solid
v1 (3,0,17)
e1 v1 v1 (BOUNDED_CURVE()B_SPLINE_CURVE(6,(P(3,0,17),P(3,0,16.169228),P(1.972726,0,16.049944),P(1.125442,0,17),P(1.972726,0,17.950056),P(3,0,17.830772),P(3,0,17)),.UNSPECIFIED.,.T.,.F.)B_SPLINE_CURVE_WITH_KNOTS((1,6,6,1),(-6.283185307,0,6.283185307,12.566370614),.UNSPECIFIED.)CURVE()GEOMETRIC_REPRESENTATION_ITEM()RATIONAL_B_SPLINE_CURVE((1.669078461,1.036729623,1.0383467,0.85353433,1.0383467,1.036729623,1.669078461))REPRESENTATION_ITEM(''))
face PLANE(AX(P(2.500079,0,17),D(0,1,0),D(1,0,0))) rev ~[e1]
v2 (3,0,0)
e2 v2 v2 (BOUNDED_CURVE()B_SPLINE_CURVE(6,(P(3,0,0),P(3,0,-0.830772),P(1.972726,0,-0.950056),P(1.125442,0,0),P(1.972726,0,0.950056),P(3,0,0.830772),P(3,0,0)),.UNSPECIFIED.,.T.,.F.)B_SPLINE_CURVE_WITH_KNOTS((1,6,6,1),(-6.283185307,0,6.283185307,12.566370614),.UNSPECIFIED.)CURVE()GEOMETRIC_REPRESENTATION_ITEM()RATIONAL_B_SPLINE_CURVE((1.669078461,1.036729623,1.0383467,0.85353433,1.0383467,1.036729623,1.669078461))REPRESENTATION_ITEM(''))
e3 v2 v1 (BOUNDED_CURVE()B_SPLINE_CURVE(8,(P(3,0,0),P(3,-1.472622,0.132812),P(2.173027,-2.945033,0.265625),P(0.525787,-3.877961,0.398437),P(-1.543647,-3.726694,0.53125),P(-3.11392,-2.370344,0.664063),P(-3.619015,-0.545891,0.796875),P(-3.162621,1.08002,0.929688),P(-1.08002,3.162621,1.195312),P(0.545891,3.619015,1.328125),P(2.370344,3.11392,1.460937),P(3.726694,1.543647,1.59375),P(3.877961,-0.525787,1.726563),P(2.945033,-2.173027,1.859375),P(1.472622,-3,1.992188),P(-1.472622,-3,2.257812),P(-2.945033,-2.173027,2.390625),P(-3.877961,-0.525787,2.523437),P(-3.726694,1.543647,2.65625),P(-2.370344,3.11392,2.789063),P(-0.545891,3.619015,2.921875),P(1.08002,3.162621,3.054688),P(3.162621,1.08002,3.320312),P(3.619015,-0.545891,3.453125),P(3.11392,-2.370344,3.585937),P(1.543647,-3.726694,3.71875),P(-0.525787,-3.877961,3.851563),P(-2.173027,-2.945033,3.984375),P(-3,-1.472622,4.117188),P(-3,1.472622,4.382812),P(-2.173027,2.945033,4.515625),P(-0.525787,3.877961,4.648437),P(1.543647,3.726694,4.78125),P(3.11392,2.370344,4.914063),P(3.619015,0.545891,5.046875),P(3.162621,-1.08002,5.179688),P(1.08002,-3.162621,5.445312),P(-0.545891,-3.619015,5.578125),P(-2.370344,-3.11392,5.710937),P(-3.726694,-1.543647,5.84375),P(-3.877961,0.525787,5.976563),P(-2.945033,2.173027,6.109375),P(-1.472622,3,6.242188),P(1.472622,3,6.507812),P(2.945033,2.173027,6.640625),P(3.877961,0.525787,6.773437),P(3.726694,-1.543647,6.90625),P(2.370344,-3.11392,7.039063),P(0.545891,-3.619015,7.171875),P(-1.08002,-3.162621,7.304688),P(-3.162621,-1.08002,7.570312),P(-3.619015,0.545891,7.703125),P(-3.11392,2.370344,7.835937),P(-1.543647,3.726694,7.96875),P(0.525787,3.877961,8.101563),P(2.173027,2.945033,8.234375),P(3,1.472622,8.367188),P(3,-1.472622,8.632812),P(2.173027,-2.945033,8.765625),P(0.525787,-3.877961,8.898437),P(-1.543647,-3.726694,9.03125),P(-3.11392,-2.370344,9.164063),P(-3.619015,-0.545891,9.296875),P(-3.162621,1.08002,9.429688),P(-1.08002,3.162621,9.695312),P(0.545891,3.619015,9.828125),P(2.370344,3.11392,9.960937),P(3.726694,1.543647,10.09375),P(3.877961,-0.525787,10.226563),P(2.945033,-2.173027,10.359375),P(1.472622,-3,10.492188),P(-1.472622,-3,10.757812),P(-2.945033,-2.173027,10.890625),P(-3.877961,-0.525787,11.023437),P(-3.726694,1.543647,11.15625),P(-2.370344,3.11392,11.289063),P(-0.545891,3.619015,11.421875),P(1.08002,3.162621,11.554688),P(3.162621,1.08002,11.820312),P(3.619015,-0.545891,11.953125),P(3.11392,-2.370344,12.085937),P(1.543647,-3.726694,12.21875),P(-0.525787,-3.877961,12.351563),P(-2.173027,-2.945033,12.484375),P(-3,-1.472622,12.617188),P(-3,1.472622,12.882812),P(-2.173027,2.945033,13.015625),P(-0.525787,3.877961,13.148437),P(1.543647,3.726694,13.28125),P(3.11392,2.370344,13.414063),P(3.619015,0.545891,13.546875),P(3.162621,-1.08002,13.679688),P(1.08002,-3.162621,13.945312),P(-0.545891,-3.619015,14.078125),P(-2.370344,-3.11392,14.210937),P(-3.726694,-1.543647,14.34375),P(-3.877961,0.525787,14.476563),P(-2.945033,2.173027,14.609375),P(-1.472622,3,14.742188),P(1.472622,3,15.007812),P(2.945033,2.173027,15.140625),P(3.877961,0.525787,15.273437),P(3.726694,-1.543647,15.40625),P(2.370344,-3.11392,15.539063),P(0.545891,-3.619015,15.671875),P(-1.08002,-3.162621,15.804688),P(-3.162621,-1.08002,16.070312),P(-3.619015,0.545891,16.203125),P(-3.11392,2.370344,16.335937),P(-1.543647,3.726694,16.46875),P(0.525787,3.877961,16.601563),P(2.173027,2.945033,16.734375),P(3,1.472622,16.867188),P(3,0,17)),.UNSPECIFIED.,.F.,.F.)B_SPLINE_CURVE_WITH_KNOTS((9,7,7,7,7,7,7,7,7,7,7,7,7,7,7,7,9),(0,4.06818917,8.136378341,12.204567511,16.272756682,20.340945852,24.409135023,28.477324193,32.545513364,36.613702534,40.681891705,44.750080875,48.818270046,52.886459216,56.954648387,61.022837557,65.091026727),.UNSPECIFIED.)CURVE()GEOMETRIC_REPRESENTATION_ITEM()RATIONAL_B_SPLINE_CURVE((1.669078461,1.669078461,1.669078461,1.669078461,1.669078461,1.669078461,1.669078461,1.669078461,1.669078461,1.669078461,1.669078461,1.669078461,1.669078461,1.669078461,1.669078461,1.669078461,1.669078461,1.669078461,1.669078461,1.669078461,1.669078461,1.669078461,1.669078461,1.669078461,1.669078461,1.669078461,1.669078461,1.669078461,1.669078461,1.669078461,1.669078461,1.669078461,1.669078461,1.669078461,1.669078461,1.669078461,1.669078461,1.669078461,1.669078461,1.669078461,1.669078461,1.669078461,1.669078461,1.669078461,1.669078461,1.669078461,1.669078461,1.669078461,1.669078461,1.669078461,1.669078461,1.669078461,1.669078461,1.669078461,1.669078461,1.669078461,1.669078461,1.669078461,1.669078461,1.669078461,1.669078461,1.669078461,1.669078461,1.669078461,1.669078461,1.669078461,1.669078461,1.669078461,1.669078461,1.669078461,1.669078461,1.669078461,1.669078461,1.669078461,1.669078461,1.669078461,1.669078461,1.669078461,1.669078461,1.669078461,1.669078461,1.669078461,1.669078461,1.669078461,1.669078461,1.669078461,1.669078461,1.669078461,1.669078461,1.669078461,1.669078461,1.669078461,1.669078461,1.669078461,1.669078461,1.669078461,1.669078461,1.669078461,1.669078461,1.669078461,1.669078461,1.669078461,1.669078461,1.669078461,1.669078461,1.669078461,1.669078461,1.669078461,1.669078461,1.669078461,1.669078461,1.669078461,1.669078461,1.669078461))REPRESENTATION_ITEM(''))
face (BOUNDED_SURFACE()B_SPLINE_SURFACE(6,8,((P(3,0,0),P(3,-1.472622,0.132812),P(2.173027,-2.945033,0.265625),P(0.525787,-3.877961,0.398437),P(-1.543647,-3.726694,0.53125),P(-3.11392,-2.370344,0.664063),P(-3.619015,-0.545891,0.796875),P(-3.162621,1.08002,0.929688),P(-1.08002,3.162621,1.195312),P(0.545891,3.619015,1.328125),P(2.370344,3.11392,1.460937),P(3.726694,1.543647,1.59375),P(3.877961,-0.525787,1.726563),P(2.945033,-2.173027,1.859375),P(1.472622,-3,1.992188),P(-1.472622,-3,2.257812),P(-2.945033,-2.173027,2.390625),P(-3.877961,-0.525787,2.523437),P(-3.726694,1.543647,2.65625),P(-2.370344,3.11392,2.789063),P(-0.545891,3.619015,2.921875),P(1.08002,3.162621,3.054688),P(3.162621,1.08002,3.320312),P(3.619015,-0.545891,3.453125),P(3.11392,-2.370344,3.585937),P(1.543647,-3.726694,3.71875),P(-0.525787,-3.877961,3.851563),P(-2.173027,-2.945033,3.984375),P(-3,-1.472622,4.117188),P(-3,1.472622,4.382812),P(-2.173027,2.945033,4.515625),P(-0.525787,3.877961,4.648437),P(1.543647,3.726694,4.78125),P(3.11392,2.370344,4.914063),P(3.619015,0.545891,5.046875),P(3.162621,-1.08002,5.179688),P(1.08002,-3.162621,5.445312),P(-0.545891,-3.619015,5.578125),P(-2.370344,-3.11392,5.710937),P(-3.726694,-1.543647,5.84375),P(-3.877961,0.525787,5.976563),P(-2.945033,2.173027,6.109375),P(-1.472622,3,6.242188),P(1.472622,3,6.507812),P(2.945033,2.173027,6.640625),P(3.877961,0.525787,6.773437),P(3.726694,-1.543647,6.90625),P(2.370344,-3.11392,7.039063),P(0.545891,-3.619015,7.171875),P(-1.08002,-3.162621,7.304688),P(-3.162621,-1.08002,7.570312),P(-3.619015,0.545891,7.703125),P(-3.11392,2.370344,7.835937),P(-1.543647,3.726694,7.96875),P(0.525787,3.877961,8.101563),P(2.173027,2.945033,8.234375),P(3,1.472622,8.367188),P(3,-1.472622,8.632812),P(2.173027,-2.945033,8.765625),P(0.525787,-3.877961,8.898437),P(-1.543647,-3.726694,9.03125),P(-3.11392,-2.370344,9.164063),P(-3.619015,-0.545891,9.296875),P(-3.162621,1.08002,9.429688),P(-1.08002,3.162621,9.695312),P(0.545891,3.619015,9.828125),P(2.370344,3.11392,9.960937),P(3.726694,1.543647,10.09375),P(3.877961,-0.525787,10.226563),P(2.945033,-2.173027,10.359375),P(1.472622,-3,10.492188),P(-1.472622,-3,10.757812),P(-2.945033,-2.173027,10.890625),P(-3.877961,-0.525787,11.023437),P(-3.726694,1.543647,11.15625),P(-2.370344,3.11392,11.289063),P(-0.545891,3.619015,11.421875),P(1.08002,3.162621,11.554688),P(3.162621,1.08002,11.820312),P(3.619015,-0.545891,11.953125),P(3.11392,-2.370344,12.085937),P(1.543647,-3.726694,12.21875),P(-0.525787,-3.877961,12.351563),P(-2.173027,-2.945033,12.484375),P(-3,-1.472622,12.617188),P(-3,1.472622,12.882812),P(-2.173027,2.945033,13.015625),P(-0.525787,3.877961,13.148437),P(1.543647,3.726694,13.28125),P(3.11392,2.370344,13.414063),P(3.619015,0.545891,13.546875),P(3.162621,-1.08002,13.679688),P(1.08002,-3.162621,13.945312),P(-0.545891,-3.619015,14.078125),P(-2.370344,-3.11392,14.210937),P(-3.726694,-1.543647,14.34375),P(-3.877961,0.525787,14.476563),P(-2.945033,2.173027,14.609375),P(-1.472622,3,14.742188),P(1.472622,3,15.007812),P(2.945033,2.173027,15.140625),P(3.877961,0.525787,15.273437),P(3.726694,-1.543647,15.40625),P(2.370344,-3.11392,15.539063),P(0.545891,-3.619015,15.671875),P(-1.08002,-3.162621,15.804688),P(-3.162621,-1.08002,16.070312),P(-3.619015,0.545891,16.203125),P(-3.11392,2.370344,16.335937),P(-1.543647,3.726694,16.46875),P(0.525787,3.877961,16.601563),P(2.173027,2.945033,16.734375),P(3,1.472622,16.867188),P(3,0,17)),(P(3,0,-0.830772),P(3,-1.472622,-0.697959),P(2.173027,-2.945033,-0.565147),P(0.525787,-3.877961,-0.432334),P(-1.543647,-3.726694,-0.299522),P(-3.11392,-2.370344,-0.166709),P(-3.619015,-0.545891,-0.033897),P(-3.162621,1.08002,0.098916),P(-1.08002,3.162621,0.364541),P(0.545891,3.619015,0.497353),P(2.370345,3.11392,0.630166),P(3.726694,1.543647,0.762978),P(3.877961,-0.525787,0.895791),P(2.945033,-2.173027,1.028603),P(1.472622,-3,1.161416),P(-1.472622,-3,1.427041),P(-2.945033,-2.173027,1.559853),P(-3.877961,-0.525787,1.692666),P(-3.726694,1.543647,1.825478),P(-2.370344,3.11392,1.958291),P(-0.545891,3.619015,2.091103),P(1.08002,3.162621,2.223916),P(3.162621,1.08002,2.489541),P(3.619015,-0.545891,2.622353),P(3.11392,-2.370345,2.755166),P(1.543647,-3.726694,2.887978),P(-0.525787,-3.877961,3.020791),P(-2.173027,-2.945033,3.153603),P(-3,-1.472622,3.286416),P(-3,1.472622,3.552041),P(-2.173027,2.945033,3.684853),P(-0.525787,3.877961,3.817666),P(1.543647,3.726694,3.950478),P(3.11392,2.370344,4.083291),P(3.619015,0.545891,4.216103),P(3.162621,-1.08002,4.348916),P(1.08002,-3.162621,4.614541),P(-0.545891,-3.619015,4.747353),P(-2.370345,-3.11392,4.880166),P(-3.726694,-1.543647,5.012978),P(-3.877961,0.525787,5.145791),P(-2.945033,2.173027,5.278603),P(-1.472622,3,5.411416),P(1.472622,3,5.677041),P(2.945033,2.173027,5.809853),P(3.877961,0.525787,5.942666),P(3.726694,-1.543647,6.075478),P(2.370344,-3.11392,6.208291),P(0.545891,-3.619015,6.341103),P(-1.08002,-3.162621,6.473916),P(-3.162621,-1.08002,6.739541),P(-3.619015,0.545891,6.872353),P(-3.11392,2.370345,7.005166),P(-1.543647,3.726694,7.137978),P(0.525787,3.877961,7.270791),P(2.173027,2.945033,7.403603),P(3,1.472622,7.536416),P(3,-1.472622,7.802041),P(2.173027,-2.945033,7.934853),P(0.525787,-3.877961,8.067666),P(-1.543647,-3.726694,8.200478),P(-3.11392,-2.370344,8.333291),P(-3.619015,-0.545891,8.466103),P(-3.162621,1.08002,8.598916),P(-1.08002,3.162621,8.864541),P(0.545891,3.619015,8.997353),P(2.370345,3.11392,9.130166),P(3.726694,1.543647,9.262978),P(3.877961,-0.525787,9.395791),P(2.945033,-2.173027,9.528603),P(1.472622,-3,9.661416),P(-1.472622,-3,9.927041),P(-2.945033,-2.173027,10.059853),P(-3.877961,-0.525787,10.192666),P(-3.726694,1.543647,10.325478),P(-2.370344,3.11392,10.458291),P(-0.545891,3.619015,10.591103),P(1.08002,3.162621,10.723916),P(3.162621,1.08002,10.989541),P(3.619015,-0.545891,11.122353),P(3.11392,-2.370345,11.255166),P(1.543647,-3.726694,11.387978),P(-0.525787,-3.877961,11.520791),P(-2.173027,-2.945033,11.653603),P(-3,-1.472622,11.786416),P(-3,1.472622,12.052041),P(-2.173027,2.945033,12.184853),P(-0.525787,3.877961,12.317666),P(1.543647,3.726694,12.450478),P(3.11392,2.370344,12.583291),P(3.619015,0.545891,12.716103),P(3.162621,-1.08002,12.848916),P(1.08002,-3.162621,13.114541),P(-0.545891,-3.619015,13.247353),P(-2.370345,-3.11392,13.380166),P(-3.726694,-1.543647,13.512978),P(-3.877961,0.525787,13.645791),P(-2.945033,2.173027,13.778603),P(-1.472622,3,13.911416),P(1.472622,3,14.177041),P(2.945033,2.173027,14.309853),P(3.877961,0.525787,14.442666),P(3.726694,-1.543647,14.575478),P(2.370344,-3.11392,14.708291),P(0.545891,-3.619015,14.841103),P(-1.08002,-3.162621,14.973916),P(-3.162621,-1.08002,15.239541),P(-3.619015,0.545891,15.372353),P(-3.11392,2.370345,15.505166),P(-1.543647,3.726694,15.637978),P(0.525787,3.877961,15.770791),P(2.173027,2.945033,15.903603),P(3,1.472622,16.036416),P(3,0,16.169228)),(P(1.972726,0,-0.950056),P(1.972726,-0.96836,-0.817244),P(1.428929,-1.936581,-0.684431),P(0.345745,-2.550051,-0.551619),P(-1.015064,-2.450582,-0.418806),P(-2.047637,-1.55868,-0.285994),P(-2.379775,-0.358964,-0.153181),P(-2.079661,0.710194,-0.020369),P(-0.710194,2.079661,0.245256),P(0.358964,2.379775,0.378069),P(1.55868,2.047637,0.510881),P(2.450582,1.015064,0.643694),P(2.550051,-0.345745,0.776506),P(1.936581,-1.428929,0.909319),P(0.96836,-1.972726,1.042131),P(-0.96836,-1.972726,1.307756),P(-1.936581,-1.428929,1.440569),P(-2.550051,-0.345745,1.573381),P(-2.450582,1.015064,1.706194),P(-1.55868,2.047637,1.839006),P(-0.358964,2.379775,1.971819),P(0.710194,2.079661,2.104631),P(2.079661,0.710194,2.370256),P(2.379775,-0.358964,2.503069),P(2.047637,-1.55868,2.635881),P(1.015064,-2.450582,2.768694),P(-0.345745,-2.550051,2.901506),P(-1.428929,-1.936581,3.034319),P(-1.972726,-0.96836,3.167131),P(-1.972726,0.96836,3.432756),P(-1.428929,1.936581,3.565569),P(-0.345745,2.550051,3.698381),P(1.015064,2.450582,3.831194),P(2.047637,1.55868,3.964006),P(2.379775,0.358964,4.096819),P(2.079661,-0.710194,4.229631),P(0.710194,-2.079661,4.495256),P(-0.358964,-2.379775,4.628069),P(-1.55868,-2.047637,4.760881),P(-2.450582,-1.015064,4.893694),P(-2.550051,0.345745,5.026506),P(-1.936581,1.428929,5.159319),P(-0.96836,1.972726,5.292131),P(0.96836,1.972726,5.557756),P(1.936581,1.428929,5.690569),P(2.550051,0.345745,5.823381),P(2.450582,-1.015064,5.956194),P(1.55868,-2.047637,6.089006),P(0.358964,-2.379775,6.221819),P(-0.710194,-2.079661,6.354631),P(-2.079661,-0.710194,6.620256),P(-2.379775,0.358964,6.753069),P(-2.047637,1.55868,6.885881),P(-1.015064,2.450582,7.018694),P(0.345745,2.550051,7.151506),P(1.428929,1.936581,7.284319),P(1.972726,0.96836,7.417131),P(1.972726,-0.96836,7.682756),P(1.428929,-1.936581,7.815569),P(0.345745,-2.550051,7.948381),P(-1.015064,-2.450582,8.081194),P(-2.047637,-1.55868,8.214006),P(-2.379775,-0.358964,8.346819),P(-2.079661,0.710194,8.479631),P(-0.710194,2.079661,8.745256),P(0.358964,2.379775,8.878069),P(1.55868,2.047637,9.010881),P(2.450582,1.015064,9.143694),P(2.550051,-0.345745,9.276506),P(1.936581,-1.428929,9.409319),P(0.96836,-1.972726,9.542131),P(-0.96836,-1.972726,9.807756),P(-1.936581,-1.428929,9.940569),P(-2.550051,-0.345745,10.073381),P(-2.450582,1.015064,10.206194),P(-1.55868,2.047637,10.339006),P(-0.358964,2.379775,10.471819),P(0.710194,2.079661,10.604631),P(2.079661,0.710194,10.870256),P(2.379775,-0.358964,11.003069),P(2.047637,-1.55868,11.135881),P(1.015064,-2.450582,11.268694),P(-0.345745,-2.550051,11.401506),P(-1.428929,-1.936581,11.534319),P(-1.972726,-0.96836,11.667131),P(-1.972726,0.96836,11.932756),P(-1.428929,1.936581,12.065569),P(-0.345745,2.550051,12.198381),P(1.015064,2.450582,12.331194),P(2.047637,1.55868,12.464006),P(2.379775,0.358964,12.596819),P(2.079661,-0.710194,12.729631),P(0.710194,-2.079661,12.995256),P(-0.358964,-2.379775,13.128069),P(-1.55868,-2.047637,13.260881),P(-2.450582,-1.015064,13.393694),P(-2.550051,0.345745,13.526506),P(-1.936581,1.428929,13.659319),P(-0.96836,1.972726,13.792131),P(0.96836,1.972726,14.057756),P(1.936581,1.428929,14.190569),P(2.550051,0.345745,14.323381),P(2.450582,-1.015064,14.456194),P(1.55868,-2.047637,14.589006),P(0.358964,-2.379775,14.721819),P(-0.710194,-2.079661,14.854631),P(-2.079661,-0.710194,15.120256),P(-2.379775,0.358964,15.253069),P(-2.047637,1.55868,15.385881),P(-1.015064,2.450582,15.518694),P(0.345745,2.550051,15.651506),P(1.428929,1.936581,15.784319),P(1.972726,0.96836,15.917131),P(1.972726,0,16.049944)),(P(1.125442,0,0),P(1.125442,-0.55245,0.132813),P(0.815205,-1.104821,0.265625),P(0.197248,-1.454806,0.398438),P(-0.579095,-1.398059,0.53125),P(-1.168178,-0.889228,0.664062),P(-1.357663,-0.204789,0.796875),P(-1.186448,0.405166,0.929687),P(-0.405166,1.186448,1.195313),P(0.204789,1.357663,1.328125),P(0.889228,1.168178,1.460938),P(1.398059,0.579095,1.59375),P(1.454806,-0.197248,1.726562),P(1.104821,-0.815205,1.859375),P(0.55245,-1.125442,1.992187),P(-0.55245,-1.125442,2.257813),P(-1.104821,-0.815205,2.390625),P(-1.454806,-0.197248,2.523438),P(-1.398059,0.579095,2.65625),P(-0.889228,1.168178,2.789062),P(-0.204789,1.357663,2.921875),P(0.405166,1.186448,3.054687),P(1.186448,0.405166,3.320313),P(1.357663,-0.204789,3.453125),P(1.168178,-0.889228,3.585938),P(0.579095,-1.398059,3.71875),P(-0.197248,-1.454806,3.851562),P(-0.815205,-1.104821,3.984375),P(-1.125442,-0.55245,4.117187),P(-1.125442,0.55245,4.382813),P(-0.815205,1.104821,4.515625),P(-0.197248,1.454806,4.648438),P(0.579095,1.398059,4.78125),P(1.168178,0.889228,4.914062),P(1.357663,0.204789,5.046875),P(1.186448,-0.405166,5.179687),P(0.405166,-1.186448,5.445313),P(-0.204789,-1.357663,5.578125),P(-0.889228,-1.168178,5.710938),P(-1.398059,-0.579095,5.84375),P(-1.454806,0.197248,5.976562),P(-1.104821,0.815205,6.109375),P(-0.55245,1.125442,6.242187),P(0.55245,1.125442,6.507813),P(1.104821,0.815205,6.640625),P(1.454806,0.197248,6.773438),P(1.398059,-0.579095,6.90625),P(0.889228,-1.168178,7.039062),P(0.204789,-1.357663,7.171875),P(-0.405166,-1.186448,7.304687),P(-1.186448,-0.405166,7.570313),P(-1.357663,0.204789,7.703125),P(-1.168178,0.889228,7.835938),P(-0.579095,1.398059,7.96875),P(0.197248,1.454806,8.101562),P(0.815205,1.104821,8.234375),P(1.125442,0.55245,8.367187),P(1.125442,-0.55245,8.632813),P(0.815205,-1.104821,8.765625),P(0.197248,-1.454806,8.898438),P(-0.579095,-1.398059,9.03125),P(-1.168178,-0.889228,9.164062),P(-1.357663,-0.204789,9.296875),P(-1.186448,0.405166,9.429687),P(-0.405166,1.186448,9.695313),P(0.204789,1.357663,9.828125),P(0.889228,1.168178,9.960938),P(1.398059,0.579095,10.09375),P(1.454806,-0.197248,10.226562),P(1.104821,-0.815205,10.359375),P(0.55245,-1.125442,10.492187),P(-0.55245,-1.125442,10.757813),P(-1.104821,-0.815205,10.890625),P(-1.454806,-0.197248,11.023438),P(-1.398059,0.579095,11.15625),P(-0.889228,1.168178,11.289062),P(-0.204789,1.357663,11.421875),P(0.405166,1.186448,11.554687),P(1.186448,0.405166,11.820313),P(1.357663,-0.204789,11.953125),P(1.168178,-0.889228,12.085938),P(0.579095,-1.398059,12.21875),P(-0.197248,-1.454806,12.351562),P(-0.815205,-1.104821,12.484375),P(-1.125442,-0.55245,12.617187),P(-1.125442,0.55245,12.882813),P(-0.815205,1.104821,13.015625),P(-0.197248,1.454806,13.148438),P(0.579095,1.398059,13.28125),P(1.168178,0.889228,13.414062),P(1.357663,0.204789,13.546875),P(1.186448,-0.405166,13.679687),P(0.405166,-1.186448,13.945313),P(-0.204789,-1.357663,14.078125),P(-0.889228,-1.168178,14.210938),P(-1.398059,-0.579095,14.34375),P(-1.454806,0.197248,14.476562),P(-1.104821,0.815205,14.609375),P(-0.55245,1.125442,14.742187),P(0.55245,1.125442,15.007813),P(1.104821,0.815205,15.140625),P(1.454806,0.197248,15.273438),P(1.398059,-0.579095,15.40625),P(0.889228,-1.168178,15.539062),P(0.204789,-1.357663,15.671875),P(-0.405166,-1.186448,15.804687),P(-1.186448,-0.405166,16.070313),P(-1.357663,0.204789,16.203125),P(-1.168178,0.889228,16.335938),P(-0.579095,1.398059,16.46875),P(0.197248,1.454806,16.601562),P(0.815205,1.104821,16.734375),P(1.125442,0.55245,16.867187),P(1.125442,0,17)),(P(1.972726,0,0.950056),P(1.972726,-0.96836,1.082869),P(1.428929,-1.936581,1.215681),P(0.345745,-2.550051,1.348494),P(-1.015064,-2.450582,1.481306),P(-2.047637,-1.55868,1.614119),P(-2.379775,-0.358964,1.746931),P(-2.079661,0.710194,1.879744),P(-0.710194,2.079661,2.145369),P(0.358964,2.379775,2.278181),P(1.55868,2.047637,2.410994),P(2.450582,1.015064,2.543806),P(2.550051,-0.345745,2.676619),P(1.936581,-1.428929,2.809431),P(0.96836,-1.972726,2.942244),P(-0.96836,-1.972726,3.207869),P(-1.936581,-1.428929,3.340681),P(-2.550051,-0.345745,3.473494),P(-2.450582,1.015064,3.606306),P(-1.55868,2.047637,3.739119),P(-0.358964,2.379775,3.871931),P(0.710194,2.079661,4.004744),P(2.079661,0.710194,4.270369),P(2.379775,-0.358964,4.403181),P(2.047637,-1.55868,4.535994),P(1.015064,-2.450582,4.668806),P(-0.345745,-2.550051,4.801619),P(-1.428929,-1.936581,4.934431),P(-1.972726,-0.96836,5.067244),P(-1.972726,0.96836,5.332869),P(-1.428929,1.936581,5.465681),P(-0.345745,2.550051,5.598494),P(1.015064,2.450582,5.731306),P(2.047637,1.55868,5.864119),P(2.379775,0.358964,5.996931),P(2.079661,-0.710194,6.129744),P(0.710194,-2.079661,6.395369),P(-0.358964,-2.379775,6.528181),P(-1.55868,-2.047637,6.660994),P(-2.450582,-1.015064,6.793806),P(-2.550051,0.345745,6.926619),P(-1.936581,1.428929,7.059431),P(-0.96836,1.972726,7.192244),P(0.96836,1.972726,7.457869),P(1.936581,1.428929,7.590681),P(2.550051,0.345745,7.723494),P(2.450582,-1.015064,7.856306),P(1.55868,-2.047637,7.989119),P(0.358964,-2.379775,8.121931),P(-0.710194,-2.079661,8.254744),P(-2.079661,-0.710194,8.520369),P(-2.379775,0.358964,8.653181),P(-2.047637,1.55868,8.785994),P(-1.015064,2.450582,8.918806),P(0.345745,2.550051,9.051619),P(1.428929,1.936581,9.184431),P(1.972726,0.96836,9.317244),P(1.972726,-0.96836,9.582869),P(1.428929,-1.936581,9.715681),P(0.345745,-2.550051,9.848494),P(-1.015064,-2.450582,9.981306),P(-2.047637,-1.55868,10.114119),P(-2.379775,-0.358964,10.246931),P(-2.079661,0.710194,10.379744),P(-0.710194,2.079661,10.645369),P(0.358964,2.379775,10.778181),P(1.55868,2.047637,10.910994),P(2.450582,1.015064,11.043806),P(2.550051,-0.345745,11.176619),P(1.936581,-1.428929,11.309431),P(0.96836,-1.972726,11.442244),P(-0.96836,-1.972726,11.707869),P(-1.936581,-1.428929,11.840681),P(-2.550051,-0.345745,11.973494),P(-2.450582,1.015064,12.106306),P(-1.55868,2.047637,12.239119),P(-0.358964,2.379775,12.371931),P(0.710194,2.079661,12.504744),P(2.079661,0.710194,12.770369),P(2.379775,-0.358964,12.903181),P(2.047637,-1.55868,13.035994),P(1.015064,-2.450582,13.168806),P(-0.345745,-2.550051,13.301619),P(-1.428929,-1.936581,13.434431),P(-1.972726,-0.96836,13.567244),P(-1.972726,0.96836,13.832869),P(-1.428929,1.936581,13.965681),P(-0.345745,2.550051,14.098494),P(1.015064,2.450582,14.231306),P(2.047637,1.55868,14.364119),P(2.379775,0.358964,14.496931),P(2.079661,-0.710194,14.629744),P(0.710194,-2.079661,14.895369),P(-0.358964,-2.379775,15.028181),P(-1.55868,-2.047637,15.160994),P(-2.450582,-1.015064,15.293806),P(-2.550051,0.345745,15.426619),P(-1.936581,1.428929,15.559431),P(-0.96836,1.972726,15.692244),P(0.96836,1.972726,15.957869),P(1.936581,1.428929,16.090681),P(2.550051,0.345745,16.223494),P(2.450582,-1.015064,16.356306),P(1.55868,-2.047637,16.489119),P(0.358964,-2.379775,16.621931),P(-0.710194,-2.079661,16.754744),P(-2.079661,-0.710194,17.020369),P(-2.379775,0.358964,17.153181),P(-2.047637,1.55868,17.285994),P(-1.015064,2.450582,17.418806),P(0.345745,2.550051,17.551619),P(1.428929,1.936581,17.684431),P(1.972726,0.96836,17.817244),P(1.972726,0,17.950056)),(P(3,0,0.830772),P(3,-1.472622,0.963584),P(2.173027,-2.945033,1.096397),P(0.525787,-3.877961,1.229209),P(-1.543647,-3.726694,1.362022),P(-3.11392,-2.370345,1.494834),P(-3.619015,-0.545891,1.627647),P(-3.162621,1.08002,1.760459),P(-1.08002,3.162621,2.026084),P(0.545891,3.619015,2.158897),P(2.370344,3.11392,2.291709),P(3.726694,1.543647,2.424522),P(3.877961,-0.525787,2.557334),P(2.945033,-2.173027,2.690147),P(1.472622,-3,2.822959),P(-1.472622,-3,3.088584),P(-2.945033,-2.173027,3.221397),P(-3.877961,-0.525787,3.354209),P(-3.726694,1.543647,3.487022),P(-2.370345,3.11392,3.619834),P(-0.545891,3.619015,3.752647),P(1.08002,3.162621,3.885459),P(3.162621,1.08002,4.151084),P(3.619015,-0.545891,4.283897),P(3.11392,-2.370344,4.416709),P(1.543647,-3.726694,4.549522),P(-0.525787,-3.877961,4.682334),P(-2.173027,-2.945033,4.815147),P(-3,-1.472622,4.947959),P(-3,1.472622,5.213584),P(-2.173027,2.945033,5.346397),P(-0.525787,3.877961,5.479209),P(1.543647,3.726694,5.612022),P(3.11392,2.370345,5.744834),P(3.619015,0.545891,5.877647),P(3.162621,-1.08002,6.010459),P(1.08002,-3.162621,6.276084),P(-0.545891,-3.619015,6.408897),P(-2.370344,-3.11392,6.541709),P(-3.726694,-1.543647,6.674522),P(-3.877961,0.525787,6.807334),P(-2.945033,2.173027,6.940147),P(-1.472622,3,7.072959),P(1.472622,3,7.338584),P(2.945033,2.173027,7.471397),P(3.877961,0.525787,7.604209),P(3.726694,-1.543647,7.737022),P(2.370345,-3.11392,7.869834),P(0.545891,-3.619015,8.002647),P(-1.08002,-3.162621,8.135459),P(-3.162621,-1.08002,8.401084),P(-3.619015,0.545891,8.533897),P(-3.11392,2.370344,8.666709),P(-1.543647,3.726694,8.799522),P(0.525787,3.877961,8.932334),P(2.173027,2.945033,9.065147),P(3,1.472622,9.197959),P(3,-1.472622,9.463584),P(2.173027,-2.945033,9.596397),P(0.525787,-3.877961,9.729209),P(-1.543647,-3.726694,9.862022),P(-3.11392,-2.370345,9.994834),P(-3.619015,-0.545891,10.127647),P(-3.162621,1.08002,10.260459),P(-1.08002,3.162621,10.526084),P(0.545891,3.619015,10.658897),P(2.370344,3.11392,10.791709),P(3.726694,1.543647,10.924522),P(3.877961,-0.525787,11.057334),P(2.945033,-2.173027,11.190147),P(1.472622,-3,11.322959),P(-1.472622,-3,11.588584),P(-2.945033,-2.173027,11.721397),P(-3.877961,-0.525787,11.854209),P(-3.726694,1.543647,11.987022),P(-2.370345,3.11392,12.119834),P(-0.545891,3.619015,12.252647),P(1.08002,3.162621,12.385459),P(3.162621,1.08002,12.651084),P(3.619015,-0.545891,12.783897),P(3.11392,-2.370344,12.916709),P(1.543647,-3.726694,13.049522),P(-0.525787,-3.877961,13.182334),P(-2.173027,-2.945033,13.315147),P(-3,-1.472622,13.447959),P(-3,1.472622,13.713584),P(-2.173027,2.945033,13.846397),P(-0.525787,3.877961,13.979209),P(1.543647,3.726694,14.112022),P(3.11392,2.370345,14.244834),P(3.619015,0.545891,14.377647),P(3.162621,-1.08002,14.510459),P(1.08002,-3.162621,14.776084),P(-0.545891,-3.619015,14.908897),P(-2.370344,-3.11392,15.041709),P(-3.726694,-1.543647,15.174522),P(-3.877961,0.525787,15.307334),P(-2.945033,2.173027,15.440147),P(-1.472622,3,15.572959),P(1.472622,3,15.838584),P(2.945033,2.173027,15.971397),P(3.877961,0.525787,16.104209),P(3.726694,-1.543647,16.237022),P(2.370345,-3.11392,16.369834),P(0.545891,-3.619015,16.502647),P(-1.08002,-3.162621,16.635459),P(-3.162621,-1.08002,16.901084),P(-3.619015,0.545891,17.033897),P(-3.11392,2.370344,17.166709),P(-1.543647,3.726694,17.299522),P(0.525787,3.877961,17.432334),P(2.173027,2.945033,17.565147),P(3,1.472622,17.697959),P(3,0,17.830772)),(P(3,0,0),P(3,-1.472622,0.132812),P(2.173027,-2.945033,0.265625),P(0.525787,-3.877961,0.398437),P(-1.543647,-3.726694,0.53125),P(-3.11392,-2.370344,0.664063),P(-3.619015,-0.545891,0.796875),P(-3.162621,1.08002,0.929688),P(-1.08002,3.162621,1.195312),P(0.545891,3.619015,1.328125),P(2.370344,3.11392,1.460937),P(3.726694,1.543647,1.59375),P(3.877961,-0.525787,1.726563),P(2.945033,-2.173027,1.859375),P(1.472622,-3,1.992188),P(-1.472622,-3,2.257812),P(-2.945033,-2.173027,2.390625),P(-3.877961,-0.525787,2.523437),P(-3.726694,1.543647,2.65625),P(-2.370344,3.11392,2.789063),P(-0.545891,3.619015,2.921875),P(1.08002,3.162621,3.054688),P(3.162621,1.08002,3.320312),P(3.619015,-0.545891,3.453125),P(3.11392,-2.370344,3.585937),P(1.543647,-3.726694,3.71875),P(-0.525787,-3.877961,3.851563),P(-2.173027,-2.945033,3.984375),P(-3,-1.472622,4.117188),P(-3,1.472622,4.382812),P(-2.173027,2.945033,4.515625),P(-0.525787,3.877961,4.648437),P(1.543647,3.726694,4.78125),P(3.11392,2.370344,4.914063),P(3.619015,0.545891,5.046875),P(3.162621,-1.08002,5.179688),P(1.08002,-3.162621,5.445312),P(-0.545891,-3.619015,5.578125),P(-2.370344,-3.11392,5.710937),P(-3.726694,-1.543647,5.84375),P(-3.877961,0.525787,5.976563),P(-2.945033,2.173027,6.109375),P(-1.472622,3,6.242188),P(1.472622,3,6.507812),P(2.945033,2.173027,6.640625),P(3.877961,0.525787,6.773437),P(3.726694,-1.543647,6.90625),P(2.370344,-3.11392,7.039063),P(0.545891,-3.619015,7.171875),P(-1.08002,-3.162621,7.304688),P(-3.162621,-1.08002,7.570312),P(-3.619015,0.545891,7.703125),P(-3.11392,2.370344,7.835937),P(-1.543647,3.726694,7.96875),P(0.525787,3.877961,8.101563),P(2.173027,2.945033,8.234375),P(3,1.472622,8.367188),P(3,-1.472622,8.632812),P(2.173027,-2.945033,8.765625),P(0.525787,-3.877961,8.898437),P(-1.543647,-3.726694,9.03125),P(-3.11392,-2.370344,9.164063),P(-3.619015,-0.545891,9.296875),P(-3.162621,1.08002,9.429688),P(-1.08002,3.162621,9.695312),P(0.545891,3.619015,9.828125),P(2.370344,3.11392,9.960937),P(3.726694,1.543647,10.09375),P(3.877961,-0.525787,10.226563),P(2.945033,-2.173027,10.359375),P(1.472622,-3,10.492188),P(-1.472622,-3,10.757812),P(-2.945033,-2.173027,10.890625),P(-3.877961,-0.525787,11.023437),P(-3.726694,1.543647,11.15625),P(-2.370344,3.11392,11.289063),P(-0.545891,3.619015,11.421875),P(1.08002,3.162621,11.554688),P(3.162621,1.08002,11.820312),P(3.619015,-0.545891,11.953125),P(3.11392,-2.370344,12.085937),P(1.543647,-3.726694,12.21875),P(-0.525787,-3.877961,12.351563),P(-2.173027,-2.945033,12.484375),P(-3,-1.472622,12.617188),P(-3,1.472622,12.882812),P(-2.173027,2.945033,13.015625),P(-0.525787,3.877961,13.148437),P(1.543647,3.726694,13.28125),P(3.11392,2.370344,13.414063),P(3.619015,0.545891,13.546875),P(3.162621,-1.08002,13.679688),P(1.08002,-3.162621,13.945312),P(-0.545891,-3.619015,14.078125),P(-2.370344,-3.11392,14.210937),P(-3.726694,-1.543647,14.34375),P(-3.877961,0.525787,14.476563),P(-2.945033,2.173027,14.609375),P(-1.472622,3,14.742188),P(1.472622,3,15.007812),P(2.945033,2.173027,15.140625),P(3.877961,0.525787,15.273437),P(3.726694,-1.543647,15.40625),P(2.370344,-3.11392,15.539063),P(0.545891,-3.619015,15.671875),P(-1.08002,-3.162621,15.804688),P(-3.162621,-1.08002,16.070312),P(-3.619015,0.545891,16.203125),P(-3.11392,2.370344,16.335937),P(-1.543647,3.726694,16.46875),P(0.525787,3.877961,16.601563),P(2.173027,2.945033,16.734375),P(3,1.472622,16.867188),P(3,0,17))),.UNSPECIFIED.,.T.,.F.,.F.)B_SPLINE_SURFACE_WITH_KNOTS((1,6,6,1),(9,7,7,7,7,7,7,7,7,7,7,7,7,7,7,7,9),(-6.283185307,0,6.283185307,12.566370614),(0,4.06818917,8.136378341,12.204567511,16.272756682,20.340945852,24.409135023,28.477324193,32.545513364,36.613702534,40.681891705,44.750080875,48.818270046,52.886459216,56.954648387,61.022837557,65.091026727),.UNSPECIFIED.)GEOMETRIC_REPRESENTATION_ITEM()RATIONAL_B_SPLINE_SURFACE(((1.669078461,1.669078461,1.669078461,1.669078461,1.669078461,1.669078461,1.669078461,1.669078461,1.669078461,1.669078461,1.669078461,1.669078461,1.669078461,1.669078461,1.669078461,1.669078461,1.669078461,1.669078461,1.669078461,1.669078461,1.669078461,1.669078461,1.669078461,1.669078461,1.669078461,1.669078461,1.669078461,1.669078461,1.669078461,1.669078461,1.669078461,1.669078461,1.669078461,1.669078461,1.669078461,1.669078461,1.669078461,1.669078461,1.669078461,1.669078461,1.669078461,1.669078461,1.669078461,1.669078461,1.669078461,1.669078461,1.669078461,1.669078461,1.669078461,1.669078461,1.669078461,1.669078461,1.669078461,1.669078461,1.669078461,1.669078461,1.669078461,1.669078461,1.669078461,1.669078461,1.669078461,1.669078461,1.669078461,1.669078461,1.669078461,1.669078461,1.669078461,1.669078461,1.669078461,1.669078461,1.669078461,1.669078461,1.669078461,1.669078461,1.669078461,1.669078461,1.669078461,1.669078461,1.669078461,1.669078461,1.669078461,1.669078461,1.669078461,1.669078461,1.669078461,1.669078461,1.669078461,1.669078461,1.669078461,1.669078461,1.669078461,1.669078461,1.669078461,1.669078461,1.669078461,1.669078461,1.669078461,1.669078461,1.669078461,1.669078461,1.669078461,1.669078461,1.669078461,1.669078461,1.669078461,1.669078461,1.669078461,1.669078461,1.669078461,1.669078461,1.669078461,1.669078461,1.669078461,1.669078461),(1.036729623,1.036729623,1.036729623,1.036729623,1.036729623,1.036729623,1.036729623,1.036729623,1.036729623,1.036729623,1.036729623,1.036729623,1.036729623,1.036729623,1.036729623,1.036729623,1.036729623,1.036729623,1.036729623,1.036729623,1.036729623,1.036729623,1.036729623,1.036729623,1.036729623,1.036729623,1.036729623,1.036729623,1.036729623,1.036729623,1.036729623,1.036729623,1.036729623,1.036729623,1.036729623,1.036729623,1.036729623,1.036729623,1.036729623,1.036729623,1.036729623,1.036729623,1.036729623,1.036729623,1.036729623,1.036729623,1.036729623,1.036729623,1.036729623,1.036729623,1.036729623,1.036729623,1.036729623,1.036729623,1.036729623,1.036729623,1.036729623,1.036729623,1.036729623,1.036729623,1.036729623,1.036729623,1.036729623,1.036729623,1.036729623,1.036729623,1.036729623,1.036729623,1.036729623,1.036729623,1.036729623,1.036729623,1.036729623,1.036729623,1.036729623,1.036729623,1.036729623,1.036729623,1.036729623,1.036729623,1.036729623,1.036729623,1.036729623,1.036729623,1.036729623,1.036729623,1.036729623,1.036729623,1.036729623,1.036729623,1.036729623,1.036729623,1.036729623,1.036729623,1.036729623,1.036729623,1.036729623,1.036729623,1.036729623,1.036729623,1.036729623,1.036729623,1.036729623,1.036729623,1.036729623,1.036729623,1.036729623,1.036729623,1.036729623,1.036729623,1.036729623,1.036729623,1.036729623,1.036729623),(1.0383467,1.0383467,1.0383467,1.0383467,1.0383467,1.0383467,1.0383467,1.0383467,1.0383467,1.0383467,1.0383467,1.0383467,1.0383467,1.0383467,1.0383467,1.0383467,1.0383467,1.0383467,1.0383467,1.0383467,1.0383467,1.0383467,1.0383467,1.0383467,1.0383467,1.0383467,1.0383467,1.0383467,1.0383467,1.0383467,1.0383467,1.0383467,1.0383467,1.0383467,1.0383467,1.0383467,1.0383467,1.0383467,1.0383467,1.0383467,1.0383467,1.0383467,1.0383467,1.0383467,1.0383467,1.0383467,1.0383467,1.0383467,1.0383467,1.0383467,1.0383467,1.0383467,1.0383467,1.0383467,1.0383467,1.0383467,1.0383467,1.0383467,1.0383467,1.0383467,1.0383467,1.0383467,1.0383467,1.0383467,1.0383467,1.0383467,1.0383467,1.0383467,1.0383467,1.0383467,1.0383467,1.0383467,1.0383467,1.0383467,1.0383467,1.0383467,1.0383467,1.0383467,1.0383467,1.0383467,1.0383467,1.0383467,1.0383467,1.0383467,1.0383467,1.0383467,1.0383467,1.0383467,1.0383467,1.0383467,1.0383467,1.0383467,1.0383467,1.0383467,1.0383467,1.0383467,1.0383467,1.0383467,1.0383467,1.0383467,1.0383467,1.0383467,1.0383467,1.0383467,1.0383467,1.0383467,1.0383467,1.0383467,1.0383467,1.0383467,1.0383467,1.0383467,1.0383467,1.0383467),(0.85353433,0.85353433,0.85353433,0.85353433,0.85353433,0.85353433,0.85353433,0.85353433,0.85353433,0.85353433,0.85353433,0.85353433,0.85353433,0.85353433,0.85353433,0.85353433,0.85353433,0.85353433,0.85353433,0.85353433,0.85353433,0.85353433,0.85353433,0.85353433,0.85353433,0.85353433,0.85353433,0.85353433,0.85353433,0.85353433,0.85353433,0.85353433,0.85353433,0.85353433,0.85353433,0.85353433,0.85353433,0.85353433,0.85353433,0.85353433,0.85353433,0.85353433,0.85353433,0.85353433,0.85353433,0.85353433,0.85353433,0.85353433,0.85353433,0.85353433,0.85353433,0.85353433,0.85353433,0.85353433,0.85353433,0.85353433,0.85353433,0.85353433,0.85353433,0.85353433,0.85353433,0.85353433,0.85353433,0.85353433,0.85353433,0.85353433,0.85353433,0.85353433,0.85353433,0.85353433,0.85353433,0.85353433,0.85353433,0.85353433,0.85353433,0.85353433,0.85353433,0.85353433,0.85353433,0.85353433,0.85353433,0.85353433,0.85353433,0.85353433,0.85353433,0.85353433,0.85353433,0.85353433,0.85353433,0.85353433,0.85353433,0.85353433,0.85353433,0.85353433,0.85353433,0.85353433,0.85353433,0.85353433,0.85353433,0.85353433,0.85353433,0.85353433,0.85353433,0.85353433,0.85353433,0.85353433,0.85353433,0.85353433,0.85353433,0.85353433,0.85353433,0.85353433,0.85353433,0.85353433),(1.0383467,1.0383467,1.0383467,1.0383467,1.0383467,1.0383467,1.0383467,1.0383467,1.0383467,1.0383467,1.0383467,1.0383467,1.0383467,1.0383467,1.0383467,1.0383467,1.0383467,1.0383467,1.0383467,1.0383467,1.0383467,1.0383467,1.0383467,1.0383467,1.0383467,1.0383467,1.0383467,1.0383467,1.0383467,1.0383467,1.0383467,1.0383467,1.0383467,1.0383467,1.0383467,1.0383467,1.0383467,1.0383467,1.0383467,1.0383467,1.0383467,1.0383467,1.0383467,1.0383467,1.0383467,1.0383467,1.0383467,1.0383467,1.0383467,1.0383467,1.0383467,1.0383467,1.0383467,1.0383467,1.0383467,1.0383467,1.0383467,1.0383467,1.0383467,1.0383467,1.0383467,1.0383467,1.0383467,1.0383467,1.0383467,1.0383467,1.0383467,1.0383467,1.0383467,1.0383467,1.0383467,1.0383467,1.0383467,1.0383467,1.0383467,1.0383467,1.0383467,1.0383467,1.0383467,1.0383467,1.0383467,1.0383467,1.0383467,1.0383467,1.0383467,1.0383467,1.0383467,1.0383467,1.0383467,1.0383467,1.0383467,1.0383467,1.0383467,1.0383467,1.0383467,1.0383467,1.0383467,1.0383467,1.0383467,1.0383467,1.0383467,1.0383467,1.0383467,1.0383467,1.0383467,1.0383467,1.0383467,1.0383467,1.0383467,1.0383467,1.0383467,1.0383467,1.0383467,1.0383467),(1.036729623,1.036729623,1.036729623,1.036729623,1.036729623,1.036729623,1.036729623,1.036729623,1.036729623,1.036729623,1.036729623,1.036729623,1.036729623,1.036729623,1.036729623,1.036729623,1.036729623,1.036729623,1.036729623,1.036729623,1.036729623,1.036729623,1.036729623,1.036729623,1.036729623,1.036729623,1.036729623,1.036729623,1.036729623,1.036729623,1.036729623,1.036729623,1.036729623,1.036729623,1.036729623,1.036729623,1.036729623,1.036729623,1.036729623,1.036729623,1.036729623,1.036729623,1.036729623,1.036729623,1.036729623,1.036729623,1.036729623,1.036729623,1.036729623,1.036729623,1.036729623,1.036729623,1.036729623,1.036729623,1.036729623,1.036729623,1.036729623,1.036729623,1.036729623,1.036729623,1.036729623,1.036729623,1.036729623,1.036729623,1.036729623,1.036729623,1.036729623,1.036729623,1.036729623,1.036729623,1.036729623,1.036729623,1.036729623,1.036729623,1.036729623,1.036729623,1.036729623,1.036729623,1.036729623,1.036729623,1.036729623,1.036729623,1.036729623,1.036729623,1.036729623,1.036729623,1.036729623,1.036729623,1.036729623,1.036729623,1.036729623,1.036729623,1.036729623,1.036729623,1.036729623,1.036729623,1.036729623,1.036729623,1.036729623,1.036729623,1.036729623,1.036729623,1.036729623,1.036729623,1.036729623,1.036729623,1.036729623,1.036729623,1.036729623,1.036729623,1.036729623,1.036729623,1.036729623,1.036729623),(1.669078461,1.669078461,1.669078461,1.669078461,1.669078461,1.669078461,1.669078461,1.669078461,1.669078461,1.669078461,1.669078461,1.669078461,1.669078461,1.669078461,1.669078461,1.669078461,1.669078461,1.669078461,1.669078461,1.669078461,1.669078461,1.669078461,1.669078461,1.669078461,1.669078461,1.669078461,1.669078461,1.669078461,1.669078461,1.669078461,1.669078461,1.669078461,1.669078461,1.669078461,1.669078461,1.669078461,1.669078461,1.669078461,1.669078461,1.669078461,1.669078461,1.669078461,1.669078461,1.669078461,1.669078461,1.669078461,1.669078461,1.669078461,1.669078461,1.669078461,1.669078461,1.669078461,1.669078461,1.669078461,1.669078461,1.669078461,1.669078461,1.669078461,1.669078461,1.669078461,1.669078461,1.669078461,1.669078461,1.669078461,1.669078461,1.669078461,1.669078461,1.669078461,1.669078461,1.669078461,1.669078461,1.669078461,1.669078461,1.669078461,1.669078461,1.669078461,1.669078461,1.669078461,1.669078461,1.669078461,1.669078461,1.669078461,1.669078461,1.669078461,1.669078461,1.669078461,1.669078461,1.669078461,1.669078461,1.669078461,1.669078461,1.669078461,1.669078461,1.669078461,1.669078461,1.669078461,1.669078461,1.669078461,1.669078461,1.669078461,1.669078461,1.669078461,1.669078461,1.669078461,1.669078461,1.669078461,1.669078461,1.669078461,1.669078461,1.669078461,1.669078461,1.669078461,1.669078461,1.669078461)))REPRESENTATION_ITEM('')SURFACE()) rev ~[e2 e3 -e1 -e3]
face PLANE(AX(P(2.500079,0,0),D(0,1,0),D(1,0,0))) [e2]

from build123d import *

# Parameters (mm, degrees)
SWEEP_1_PITCH  = 1.7
SWEEP_1_HEIGHT = 17
SWEEP_1_RADIUS = 2.5
SKETCH_2_R     = 0.5


with BuildPart() as part:
    # 扫描1: sweep along a helix
    with BuildLine() as sweep_1_path:
        Helix(SWEEP_1_PITCH, SWEEP_1_HEIGHT, SWEEP_1_RADIUS, center=(0, 0, 0), direction=(0, 0, 1), lefthand=True)
    # 草图2 → 扫描1 (sweep)
    with BuildSketch(Plane(origin=(0, 0, 0), x_dir=(1, 0, 0), z_dir=(0, 1, 0))):
        with Locations((2.5, 0)):
            Circle(SKETCH_2_R)
    sweep(path=sweep_1_path.line, is_frenet=True)


solid = part.part
